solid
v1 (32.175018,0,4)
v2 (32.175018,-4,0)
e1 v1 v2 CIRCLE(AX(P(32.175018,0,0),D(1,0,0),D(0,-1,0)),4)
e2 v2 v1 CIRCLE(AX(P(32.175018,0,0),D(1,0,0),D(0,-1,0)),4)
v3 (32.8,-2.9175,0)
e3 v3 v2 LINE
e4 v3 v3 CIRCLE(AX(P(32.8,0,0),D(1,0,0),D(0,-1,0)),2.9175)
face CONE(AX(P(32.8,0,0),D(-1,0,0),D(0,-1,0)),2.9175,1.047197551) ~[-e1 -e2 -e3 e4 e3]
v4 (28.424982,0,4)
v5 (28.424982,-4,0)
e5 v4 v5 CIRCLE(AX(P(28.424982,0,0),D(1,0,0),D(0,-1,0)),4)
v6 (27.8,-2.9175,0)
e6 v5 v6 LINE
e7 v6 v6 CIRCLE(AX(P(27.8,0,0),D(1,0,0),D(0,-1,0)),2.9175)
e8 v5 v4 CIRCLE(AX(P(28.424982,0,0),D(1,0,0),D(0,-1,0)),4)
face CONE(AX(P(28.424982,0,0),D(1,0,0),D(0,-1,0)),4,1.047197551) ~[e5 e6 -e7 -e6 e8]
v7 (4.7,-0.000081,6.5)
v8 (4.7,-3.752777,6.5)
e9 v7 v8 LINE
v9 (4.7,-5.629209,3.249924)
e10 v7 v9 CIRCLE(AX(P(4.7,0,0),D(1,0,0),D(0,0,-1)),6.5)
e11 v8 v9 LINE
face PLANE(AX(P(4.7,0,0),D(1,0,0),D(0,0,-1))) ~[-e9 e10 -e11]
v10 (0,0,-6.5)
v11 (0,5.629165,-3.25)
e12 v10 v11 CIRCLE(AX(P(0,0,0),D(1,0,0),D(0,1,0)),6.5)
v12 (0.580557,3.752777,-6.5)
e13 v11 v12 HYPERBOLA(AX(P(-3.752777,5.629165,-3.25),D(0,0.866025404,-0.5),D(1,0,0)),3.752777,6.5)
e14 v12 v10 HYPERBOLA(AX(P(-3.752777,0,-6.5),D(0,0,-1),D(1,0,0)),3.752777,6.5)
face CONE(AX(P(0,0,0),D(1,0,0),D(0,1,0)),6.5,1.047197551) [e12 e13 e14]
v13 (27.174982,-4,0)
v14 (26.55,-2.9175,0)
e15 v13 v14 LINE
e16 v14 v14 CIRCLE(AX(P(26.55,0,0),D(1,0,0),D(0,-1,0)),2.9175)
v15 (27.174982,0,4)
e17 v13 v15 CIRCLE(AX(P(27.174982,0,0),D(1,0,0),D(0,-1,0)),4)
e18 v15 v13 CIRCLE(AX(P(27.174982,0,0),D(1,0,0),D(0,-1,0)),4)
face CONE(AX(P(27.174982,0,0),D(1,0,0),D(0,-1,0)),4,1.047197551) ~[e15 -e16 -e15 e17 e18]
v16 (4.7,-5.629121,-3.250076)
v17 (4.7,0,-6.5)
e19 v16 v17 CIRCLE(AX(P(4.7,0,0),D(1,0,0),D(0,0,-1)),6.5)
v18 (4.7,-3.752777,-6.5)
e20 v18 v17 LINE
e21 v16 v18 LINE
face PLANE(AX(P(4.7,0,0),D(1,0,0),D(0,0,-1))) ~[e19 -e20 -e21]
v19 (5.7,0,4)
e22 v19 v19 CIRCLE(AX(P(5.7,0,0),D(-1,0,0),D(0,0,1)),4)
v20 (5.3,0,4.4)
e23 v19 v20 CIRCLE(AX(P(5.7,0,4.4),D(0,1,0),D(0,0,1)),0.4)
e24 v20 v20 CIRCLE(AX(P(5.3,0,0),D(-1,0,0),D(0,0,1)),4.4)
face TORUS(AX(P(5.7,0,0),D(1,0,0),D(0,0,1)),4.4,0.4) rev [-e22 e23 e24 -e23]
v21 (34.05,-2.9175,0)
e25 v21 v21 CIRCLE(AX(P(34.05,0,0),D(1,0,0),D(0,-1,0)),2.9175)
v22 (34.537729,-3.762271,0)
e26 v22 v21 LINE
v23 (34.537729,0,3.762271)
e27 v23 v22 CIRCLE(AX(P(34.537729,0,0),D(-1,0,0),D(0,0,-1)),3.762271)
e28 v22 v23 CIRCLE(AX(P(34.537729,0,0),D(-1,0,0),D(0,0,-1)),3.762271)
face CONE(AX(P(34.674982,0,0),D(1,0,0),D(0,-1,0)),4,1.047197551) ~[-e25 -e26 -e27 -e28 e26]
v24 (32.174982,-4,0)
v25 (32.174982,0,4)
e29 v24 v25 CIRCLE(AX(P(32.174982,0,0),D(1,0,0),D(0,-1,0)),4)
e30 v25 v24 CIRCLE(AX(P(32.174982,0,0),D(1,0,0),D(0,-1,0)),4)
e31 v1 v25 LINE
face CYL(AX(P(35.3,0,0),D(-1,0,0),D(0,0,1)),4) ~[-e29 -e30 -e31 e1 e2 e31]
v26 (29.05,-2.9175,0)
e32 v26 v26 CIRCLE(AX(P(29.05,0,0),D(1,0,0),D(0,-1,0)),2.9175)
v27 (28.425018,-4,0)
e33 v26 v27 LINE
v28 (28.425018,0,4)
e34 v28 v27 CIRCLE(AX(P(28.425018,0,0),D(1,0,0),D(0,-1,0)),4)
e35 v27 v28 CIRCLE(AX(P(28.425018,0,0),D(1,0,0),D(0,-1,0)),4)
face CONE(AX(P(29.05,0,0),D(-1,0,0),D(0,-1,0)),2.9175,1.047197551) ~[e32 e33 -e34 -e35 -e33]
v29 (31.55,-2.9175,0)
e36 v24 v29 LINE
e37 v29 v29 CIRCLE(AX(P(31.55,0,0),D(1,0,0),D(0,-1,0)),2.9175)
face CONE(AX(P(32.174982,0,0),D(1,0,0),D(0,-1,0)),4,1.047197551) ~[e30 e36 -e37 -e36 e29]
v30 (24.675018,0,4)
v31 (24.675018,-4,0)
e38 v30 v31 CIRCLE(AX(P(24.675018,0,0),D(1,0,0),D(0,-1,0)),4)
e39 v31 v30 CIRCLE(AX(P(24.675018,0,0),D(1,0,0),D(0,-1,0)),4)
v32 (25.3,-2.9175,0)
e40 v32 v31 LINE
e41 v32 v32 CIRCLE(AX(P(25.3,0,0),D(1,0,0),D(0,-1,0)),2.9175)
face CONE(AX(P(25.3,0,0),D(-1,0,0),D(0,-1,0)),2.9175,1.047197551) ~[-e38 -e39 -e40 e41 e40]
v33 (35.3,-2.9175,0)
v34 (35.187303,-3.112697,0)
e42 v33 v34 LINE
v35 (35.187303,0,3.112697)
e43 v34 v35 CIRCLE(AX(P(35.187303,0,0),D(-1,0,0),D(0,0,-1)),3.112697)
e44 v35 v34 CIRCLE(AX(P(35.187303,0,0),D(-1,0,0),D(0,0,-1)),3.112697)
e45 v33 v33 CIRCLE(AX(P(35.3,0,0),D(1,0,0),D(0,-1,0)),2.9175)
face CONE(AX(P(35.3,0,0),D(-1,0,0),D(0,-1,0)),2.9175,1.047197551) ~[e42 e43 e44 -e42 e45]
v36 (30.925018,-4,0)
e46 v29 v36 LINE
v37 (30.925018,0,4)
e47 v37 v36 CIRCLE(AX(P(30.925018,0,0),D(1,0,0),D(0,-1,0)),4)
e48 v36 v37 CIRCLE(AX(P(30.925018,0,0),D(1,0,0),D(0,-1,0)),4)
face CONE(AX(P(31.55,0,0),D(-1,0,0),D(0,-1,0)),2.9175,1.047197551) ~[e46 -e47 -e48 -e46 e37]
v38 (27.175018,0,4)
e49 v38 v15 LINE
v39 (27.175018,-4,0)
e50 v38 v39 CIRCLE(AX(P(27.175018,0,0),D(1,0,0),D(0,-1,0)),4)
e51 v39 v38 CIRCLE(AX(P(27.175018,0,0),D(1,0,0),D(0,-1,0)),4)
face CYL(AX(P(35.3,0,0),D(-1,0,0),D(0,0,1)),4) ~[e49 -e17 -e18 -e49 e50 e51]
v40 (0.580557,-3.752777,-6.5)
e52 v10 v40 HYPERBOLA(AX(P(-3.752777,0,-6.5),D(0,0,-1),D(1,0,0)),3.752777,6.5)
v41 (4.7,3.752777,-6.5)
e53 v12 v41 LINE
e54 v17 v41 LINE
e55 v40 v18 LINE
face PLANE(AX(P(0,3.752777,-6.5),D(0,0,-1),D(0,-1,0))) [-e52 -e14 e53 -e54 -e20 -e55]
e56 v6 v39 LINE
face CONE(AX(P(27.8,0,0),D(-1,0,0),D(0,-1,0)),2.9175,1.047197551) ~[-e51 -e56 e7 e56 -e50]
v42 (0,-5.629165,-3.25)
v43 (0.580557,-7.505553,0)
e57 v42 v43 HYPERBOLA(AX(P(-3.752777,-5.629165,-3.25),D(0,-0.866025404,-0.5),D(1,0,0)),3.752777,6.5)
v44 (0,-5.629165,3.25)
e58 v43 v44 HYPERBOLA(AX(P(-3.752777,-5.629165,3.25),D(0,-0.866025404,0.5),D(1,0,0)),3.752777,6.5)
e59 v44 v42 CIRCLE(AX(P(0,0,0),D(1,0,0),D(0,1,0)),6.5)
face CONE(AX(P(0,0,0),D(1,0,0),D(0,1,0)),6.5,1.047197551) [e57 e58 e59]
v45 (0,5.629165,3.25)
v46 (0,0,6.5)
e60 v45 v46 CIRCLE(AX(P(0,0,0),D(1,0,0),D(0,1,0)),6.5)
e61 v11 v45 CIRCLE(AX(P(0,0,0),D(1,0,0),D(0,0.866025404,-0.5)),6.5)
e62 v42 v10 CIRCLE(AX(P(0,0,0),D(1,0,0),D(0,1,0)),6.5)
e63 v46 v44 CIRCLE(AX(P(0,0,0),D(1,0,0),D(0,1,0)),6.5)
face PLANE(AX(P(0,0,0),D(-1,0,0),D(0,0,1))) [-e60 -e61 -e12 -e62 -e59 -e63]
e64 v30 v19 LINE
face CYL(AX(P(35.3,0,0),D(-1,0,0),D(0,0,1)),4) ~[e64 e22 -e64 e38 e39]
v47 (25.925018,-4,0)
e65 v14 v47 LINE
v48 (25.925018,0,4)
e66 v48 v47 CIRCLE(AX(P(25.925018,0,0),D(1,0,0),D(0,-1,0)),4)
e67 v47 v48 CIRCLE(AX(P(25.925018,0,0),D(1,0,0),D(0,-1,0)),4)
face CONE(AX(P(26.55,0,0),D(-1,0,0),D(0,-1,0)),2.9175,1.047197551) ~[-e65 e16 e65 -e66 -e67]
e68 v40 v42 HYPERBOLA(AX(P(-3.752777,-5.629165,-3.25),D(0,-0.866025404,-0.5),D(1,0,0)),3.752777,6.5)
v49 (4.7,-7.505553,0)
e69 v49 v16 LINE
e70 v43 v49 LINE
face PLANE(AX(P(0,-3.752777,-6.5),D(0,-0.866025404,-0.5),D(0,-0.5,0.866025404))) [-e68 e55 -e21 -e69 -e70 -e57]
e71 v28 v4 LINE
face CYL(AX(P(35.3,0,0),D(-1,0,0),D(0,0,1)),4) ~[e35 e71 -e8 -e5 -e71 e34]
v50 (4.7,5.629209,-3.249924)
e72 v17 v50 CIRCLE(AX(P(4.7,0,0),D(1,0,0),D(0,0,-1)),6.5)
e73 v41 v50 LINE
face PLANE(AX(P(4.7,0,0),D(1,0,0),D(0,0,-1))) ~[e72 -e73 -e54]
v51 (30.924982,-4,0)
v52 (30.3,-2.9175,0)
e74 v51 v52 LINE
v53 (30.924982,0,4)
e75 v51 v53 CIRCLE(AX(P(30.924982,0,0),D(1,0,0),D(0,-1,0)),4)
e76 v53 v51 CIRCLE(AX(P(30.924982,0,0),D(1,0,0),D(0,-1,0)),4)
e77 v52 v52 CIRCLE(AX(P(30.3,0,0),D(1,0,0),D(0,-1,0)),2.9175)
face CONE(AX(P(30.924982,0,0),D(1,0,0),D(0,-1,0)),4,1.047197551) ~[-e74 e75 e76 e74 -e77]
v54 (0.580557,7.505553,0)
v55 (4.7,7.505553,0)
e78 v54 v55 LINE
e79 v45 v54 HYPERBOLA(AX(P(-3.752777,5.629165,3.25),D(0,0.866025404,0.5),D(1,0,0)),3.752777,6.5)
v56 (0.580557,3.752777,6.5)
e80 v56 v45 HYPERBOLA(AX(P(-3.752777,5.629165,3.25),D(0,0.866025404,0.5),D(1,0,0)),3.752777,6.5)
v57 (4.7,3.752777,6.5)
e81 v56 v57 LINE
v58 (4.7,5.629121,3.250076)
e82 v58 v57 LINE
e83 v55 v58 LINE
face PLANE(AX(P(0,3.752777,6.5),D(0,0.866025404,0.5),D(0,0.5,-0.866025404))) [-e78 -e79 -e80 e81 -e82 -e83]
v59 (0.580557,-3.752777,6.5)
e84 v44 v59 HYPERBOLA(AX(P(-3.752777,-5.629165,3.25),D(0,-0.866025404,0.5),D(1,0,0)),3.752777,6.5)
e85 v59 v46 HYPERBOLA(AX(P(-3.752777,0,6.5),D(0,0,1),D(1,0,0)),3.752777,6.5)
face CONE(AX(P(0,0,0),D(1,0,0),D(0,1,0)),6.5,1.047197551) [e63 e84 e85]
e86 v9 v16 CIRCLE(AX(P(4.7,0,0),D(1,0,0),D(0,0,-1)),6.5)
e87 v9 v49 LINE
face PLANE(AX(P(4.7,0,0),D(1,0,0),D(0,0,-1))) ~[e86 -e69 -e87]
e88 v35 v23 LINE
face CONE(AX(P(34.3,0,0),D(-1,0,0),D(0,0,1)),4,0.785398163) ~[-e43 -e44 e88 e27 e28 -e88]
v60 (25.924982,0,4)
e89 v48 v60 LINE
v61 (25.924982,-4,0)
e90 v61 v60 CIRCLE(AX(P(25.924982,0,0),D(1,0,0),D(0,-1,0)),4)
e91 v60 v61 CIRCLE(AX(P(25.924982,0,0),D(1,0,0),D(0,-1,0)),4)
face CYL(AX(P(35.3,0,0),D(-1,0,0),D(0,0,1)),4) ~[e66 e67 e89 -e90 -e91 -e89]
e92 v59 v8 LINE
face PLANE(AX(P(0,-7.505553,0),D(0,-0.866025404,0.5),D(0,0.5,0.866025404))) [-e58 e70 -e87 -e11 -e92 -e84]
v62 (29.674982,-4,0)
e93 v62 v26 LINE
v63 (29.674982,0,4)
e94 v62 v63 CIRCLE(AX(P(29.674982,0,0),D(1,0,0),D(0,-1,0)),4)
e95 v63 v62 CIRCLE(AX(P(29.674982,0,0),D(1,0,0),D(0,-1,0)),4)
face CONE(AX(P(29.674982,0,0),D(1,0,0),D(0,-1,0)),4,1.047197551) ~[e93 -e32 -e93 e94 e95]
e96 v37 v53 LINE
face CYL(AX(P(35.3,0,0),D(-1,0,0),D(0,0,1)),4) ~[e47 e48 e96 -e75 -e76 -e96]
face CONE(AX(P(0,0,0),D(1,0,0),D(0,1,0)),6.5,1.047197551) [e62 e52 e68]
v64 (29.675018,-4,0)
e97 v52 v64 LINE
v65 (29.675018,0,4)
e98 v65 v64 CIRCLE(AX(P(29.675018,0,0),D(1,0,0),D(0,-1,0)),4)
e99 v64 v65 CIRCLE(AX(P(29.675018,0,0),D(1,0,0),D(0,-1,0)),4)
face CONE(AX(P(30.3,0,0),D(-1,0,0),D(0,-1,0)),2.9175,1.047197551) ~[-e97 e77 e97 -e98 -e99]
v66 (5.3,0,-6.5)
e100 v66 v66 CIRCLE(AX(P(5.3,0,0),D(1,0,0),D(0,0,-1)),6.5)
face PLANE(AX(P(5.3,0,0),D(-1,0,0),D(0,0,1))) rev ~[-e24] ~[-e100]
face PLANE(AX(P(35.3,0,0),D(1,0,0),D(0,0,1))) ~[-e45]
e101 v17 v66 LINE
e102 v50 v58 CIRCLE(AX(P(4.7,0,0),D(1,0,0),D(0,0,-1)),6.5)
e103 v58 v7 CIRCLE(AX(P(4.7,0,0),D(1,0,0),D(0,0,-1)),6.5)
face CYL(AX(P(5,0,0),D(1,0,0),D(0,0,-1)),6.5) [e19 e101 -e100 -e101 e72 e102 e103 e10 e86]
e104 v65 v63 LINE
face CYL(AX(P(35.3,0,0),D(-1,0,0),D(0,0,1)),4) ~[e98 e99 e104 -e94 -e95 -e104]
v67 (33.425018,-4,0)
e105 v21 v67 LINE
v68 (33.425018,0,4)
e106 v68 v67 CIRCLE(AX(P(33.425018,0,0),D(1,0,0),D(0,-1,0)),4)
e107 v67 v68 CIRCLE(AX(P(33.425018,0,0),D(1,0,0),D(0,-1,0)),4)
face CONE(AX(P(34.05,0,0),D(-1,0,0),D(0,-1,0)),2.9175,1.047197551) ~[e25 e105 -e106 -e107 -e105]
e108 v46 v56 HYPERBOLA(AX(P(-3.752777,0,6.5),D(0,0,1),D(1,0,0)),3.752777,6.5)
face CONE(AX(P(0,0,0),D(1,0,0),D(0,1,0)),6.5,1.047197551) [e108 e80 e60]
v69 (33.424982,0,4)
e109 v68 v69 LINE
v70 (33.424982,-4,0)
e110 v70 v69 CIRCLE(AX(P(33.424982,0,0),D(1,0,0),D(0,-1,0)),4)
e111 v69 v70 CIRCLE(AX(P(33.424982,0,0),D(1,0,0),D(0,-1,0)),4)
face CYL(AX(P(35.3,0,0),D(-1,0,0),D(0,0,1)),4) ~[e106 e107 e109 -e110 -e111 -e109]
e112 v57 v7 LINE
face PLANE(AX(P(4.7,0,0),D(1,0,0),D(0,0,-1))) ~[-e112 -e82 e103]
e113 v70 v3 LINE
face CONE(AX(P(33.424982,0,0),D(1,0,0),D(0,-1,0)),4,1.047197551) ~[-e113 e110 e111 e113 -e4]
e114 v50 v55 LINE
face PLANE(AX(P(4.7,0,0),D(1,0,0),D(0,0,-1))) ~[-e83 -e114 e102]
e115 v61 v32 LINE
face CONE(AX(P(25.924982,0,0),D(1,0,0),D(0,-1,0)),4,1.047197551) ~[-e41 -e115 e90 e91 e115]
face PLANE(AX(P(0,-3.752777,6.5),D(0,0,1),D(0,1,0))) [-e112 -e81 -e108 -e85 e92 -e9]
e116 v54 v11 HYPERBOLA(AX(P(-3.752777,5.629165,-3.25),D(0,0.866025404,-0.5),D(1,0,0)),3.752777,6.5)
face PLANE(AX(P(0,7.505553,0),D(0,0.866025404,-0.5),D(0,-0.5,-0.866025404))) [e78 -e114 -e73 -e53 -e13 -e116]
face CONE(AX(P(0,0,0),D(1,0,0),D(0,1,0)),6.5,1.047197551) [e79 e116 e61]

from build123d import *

# Parameters (mm, degrees)
EXTRUDE_378_DEPTH      = 5.3
SKETCH_4_W             = 0.6
SKETCH_4_H             = 11.005553499
CHAMFER_2060_SIZE      = 1
FILLET_2105_R          = 0.4
PATTERN_LINEAR_1_COUNT = 9
PATTERN_LINEAR_1_PITCH = 1.25


with BuildPart() as part:
    # 草图1 → Extrude 378 (new body)
    with BuildSketch(Plane(origin=(0, 0, 0), x_dir=(0, 0, -1), z_dir=(1, 0, 0))):
        Polygon((6.5, 3.75277675), (6.5, -3.75277675), (0, -7.505553499), (-6.5, -3.75277675), (-6.5, 3.75277675), (0, 7.505553499), align=None)
    extrude(amount=EXTRUDE_378_DEPTH)

    # 草图2 → 凸台-旋转1 (revolve)
    with BuildSketch(Plane.XY, mode=Mode.PRIVATE) as revolve_1_sk:
        Polygon((0, 0), (35.3, 0), (35.3, 2.9175), (35.3, 4), (7.791693541, 4), (0, 4), align=None)
    revolve(revolve_1_sk.sketch.rotate(Axis((0, 0, 0), (1, 0, 0)), 90), axis=Axis((0, 0, 0), (1, 0, 0)))

    # 草图3 → 切除-旋转1 (revolve, cut)
    with BuildSketch(Plane.XY):
        Polygon((0, 6.5), (3.46730793, 12.505553499), (3.46730793, 17.505553499), (-10, 17.505553499), (-10, 6.5), align=None)
    revolve(axis=Axis((0, 0, 0), (1, 0, 0)), mode=Mode.SUBTRACT)

    # 草图5 → 切除-旋转2 (revolve, cut)
    with BuildSketch(Plane.XY):
        Polygon((5.3, 6.5), (1.83269207, 12.505553499), (1.83269207, 17.505553499), (11.83269207, 17.505553499), (11.83269207, 6.5), align=None)
    revolve(axis=Axis((0, 0, 0), (1, 0, 0)), mode=Mode.SUBTRACT)

    # 草图4 → 切除-旋转3 (revolve, cut)
    with BuildSketch(Plane.XY, mode=Mode.PRIVATE) as cut_revolve_3_sk:
        with Locations((5, 12.00277675)):
            Rectangle(SKETCH_4_W, SKETCH_4_H)
    revolve(cut_revolve_3_sk.sketch.rotate(Axis((0, 0, 0), (1, 0, 0)), 270), axis=Axis((0, 0, 0), (1, 0, 0)), mode=Mode.SUBTRACT)

    # Chamfer 2060
    chamfer_2060_edges = [part.edges().sort_by_distance(p)[0] for p in [
        (35.3, 0, -4),
    ]]
    chamfer(chamfer_2060_edges, length=CHAMFER_2060_SIZE)

    # Fillet 2105
    fillet_2105_edges = [part.edges().sort_by_distance(p)[0] for p in [
        (5.3, 0, -4),
    ]]
    fillet(fillet_2105_edges, radius=FILLET_2105_R)

    # 草图6 → 切除-旋转4 (revolve, cut)
    with BuildSketch(Plane.XY):
        Polygon((25.3, -2.9175), (24.675018334, -4), (24.675018334, -5), (25.924981666, -5), (25.924981666, -4), align=None)
    cut_revolve_4 = revolve(axis=Axis((-3.175, 0, 0), (1, 0, 0)), mode=Mode.SUBTRACT)

    # 阵列(线性)1: 切除-旋转4 ×9
    with Locations(*[(i * PATTERN_LINEAR_1_PITCH, 0, 0) for i in range(1, PATTERN_LINEAR_1_COUNT)]):
        add(cut_revolve_4, mode=Mode.SUBTRACT)


solid = part.part
